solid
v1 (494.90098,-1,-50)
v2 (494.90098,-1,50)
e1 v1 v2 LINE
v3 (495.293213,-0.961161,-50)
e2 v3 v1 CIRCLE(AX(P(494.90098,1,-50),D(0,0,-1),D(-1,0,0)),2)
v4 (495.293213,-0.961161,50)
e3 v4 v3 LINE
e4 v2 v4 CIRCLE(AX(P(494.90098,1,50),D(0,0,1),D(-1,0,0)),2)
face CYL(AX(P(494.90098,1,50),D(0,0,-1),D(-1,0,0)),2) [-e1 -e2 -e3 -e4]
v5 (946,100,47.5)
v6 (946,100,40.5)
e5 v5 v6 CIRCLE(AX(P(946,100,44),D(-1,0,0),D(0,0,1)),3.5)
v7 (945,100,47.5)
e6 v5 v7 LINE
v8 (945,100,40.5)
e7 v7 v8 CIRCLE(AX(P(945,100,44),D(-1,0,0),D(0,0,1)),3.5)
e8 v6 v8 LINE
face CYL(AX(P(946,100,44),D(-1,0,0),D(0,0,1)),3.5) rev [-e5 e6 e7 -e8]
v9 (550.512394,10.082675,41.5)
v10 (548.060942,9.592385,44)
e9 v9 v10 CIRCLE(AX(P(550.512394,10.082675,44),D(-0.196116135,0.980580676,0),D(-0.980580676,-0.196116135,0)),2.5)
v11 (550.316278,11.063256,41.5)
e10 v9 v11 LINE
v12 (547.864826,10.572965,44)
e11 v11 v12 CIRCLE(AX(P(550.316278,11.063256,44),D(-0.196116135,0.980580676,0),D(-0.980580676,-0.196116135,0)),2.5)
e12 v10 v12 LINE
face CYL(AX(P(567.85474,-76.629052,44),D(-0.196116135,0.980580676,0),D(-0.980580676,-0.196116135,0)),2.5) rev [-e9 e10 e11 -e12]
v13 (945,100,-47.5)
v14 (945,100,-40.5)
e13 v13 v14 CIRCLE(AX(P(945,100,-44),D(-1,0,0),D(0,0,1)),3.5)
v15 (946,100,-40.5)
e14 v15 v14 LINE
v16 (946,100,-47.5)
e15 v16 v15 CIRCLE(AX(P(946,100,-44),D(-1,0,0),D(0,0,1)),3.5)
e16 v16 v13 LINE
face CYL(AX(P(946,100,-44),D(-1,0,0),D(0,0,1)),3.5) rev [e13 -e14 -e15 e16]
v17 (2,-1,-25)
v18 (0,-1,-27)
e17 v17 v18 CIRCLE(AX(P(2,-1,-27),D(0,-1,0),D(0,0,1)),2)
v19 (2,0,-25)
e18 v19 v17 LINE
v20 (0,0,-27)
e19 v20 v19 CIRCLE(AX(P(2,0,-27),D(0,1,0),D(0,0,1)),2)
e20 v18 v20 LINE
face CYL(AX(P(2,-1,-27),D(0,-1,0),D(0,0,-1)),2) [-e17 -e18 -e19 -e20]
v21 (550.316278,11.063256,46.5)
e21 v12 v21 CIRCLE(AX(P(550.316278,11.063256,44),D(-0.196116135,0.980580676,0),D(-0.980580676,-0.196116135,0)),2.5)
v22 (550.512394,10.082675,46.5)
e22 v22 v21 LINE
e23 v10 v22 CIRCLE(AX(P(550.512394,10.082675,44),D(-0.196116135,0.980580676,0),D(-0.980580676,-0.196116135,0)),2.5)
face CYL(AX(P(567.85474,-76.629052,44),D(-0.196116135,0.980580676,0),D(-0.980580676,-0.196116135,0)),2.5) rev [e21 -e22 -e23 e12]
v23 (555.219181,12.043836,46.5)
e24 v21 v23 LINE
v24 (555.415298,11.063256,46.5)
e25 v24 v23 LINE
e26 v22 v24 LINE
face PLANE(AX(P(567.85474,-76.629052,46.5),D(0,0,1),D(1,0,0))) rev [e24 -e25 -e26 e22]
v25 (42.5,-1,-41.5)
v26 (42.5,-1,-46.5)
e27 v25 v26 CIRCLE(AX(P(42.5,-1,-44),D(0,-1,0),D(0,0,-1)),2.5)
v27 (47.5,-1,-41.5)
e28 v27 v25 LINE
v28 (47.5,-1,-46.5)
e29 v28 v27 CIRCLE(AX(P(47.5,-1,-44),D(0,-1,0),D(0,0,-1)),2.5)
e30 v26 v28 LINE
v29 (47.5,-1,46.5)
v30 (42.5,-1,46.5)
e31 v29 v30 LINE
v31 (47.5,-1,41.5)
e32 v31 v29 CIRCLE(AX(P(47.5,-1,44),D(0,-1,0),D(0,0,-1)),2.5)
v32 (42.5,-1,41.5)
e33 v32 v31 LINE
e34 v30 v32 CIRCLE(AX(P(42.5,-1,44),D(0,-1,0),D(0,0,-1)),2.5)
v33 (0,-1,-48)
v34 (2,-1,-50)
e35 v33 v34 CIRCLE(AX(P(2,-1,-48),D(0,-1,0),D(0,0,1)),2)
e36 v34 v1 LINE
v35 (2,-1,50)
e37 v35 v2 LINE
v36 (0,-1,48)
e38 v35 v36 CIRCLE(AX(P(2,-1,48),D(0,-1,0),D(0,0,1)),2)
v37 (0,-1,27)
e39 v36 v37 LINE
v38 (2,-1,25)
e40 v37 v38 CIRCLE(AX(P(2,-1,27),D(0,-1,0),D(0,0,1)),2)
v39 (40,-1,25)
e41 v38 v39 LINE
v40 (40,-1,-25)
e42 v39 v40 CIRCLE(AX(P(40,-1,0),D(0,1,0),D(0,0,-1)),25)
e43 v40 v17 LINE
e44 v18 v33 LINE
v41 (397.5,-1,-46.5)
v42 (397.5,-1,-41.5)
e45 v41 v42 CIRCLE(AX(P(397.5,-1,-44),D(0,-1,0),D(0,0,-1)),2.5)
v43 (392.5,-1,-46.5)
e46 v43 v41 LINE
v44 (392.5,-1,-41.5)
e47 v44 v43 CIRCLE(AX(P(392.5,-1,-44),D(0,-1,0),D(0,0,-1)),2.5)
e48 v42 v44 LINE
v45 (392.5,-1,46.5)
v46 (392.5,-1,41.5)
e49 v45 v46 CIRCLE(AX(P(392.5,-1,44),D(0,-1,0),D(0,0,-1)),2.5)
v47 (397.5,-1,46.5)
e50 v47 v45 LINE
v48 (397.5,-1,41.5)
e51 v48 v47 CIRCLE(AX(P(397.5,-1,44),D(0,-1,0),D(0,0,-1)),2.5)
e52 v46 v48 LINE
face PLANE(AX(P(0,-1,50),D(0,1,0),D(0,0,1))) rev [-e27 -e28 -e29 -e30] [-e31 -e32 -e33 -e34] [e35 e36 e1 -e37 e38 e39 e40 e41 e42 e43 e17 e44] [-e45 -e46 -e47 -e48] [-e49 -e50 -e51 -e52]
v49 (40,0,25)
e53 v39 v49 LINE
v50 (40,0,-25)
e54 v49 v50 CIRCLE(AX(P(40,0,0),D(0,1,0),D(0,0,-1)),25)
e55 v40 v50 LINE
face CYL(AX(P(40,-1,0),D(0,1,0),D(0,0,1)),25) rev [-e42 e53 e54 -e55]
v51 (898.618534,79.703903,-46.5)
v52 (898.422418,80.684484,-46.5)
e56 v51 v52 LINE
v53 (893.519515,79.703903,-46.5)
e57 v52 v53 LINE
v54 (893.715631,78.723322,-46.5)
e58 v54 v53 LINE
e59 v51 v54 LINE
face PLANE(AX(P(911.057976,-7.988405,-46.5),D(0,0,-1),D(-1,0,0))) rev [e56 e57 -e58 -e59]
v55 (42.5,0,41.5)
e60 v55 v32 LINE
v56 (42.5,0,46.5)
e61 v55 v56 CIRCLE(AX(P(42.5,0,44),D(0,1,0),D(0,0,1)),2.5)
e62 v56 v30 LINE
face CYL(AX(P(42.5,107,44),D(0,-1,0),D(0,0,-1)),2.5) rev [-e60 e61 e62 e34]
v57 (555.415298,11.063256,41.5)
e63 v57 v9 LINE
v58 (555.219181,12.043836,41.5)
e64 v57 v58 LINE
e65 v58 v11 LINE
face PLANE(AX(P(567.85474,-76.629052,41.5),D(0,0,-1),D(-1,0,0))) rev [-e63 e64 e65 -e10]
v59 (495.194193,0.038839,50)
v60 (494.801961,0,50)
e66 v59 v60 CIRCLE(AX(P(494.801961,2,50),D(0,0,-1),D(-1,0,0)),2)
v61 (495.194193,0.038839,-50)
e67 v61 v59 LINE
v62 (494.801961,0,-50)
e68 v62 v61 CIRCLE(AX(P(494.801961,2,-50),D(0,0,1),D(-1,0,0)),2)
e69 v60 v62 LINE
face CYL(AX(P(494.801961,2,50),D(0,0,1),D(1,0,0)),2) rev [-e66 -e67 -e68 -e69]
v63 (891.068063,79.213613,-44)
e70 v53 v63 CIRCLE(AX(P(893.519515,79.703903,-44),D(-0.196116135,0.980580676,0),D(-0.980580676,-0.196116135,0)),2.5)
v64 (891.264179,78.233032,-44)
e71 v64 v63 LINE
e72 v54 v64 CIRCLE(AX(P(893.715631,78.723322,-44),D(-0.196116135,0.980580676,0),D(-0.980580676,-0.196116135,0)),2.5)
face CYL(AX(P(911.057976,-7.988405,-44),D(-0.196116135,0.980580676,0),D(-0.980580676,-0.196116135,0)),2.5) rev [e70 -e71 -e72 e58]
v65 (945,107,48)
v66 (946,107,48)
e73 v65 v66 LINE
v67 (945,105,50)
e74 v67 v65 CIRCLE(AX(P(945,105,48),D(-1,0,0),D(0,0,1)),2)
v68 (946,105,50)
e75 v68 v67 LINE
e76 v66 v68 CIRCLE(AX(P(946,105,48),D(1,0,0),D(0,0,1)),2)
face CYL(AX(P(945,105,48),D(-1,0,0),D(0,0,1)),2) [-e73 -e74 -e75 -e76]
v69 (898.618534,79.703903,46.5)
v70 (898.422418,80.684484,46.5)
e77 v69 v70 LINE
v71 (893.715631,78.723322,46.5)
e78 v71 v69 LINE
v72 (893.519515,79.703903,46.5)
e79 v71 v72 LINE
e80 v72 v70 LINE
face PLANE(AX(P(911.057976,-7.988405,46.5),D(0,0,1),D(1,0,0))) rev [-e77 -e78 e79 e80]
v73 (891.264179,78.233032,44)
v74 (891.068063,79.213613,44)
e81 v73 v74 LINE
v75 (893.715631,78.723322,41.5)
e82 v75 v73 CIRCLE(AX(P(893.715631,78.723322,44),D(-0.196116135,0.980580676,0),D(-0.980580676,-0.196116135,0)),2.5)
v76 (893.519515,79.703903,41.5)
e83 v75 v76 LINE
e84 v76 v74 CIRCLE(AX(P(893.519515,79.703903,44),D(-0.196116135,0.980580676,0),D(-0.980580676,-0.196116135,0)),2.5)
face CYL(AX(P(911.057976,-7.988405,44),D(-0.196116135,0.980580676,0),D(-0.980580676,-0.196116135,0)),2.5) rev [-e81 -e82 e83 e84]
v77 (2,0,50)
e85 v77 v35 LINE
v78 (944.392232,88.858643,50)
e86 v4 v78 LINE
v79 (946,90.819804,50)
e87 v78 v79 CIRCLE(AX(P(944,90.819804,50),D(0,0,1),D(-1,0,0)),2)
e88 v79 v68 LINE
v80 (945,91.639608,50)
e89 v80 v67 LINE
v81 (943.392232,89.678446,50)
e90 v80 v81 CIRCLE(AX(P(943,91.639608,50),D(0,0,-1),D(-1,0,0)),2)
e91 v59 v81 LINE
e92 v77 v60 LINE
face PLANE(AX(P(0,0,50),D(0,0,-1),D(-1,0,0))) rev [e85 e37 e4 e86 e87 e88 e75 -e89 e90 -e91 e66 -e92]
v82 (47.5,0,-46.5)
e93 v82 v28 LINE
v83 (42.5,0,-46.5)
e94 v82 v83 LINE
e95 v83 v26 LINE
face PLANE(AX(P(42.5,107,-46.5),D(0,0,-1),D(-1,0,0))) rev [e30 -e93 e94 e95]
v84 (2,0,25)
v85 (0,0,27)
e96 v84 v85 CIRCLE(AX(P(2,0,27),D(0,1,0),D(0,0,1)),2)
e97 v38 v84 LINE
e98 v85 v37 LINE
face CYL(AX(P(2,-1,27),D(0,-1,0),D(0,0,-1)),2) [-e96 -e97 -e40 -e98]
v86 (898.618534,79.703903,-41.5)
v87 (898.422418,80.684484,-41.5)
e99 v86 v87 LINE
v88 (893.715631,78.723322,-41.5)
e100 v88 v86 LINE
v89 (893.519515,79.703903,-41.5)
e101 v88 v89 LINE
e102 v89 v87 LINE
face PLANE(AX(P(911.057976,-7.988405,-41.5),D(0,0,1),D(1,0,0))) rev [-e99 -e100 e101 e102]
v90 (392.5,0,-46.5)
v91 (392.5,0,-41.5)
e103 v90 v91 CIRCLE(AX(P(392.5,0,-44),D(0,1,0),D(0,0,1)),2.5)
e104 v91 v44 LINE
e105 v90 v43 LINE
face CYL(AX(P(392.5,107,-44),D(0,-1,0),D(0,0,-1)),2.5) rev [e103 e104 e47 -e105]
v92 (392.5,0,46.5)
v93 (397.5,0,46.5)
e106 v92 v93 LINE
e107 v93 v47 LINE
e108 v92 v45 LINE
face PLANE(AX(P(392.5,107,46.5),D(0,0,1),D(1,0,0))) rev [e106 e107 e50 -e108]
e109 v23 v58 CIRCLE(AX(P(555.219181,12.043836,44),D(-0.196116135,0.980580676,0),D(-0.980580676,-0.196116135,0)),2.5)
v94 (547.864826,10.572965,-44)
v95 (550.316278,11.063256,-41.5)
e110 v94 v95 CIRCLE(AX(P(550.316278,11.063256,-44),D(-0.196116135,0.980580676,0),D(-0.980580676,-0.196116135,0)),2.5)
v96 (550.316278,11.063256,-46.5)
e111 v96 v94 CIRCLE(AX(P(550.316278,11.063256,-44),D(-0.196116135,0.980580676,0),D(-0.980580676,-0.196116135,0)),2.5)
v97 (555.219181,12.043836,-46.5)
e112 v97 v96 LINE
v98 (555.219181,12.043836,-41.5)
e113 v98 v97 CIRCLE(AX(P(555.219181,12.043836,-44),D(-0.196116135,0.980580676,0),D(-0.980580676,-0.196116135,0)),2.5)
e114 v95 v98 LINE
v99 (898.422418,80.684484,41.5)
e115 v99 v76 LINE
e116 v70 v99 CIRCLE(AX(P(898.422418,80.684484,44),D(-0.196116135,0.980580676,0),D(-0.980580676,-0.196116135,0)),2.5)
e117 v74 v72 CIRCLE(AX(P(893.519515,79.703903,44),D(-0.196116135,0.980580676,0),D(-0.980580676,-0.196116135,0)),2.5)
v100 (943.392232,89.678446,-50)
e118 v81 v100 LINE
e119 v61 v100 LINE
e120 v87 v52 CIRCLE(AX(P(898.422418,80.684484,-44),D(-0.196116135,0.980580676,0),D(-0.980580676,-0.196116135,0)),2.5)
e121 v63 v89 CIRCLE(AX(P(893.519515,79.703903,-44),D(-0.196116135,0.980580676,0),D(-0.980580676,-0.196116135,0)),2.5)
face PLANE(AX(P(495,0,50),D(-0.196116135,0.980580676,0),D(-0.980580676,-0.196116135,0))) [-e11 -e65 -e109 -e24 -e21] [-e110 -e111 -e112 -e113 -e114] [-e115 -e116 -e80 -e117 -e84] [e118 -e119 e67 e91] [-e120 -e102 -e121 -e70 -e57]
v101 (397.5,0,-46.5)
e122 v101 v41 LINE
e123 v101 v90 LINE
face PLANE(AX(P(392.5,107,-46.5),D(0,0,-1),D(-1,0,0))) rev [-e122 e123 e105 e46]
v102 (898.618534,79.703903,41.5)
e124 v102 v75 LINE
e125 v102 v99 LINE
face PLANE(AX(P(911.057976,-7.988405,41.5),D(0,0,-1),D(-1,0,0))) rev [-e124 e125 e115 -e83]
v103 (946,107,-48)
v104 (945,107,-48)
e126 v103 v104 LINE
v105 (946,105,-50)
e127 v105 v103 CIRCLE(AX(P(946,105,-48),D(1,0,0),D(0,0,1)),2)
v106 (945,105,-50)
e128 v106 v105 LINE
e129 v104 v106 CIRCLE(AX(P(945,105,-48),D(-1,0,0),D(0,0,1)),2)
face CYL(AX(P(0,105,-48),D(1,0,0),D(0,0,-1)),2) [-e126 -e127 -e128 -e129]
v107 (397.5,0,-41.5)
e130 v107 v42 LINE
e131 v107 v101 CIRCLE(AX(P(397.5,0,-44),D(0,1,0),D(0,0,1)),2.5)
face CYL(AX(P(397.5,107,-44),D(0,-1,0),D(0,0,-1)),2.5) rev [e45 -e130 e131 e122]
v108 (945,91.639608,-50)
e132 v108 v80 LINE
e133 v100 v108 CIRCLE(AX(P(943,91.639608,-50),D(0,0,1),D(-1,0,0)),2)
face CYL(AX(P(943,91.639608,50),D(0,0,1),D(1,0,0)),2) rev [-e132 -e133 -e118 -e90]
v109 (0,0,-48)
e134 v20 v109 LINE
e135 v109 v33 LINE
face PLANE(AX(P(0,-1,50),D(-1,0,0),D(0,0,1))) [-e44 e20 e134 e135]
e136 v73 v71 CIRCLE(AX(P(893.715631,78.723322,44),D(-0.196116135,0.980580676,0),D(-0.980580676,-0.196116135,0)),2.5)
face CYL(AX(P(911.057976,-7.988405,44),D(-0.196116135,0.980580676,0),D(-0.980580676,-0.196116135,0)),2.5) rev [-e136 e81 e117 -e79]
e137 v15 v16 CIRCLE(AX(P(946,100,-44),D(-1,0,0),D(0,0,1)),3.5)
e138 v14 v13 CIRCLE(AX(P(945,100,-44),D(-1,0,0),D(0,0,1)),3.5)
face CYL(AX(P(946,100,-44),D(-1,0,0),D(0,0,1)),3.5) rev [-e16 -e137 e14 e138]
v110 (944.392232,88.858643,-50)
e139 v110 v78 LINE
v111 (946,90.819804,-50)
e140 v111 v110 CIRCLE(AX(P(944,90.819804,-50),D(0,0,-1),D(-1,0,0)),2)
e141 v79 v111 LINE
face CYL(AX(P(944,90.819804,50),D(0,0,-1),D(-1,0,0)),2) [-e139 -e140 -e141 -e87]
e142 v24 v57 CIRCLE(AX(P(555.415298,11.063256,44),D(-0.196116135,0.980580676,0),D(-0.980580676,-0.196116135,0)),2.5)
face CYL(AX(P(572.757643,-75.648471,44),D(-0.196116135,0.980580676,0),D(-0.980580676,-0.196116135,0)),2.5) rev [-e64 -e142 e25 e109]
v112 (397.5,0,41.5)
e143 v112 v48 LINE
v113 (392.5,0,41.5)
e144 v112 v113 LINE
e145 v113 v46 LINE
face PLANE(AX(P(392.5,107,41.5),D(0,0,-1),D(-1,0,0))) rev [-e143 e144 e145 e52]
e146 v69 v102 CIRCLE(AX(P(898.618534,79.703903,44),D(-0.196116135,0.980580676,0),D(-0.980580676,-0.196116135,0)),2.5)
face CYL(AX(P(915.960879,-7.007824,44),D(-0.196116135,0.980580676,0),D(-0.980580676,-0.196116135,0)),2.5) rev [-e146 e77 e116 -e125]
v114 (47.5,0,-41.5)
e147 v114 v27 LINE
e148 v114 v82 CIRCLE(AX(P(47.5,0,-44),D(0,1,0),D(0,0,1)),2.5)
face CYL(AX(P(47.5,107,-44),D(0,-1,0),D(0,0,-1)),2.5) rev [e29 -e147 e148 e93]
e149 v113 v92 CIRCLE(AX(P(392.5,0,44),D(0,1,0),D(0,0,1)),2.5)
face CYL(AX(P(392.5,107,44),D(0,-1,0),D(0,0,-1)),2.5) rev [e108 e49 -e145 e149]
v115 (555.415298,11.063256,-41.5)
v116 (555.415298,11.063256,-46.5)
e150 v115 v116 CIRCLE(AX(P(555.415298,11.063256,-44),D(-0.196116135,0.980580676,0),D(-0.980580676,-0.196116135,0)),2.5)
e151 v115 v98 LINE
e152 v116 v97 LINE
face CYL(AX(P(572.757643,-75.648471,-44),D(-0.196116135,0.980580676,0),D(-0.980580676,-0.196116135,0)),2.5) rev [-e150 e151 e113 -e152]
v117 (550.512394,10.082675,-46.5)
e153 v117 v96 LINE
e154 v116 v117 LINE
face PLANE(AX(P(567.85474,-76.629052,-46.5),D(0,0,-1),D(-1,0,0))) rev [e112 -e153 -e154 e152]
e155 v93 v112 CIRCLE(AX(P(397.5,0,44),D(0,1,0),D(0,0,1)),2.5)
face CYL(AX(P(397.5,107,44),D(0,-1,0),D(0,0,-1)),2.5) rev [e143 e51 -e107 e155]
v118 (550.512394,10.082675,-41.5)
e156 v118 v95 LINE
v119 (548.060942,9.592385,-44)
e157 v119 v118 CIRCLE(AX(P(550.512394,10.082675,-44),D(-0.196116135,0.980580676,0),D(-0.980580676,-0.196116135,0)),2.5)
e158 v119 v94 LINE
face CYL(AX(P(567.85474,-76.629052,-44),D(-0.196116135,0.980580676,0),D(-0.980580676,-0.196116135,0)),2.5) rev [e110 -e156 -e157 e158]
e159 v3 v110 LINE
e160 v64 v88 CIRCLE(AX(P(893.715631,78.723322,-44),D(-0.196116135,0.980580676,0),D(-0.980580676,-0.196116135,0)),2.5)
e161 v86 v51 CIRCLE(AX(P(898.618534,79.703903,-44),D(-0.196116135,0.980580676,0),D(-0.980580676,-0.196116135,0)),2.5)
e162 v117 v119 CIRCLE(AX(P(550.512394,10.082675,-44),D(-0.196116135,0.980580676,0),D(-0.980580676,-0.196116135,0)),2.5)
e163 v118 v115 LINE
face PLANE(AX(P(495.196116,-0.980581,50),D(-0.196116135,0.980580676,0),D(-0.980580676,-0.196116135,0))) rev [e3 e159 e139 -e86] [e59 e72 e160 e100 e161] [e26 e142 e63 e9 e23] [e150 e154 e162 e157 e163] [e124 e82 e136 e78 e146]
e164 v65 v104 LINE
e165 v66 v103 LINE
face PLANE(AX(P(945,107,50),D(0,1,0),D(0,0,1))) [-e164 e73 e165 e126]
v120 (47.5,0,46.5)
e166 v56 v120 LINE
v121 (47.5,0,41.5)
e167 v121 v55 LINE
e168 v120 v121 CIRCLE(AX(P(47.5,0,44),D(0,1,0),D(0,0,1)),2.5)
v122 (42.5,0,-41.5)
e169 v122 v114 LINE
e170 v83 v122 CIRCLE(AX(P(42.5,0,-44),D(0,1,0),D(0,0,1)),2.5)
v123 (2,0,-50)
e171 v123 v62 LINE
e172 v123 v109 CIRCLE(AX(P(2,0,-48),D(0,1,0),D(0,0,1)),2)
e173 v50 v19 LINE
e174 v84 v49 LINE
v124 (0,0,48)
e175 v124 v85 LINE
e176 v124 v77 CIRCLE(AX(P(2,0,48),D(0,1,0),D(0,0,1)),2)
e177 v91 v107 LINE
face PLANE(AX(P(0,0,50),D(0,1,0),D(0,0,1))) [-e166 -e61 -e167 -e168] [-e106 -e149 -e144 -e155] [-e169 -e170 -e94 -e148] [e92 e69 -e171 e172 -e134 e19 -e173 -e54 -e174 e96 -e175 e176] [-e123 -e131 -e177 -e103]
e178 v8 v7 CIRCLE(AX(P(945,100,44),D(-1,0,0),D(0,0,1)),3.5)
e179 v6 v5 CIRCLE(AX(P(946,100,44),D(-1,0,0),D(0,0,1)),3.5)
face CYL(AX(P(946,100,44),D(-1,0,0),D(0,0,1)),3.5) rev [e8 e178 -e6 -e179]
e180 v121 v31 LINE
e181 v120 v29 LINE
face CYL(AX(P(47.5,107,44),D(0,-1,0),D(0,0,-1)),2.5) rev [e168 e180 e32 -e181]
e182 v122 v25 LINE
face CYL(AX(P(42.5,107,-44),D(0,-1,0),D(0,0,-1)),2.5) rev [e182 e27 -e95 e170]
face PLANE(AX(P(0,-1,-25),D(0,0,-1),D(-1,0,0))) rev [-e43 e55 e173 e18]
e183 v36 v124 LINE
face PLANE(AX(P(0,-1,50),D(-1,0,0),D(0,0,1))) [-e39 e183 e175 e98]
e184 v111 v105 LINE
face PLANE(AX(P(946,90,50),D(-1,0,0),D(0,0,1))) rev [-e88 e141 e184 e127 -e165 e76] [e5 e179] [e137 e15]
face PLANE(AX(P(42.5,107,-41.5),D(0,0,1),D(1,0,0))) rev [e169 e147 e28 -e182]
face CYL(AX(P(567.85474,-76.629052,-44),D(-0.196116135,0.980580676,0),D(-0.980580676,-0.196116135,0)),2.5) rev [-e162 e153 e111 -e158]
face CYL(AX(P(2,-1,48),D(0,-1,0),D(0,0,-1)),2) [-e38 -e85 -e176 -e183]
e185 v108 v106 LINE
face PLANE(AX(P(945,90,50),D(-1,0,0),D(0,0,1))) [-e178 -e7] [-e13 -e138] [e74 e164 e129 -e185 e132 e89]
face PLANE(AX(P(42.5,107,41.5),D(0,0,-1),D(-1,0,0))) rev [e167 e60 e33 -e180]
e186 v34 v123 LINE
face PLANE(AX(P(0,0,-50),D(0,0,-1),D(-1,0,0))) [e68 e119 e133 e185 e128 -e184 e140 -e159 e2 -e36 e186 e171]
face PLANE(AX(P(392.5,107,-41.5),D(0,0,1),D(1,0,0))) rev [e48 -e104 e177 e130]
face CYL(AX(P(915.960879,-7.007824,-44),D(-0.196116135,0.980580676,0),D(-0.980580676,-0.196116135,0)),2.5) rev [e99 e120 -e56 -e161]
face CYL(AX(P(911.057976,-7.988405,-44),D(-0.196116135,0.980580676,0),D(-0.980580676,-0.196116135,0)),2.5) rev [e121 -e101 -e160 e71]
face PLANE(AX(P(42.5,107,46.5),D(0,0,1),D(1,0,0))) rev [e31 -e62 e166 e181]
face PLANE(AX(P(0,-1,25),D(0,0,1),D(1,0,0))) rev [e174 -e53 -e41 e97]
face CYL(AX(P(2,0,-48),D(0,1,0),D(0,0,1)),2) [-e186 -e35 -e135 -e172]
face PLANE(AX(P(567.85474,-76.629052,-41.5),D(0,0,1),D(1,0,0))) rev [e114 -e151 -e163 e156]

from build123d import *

# Parameters (mm, degrees)
EXTRUDE_THIN1_DEPTH = 50
SKETCH2_R           = 3.5
CUT_EXTRUDE1_DEPTH  = 953.351825745
CUT_EXTRUDE2_DEPTH  = 954.456868453
CUT_EXTRUDE3_DEPTH  = 951.073377733
CUT_EXTRUDE4_DEPTH  = 954.344114158
FILLET1_R           = 2


with BuildPart() as part:
    # Sketch1 → Extrude-Thin1 (new, symmetric)
    with BuildSketch(Plane.XY):
        Polygon((0, 0), (495, 0), (945, 90), (945, 107), (946, 107), (946, 89.180196097), (495.099019514, -1), (0, -1), align=None)
    extrude(amount=EXTRUDE_THIN1_DEPTH, both=True)

    # Sketch2 → Cut-Extrude1 (cut, through all)
    with BuildSketch(Plane.ZY.offset(-945)):
        with Locations((-44, 100)):
            Circle(SKETCH2_R)
        with Locations((44, 100)):
            Circle(SKETCH2_R)
    extrude(amount=-CUT_EXTRUDE1_DEPTH, mode=Mode.SUBTRACT)

    # Sketch3 → Cut-Extrude2 (cut, through all)
    with BuildSketch(Plane.XZ.offset(1)):
        with BuildLine():
            Line((42.5, 46.5), (47.5, 46.5))
            ThreePointArc((47.5, 46.5), (50, 44), (47.5, 41.5))
            Line((47.5, 41.5), (42.5, 41.5))
            ThreePointArc((42.5, 41.5), (40, 44), (42.5, 46.5))
        make_face()
        with BuildLine():
            Line((42.5, -41.5), (47.5, -41.5))
            ThreePointArc((47.5, -41.5), (50, -44), (47.5, -46.5))
            Line((47.5, -46.5), (42.5, -46.5))
            ThreePointArc((42.5, -46.5), (40, -44), (42.5, -41.5))
        make_face()
        with BuildLine():
            Line((392.5, -41.5), (397.5, -41.5))
            ThreePointArc((397.5, -41.5), (400, -44), (397.5, -46.5))
            Line((397.5, -46.5), (392.5, -46.5))
            ThreePointArc((392.5, -46.5), (390, -44), (392.5, -41.5))
        make_face()
        with BuildLine():
            Line((392.5, 46.5), (397.5, 46.5))
            ThreePointArc((397.5, 46.5), (400, 44), (397.5, 41.5))
            Line((397.5, 41.5), (392.5, 41.5))
            ThreePointArc((392.5, 41.5), (390, 44), (392.5, 46.5))
        make_face()
    extrude(amount=-CUT_EXTRUDE2_DEPTH, mode=Mode.SUBTRACT)

    # Sketch4 → Cut-Extrude3 (cut, through all)
    with BuildSketch(Plane(origin=(19.038461538, -95.192307692, 0), x_dir=(0.9805806756909202, 0.1961161351381841, 0), z_dir=(-0.1961161351381841, 0.9805806756909202, 0))):
        with BuildLine():
            Line((541.79919069, 46.5), (546.79919069, 46.5))
            ThreePointArc((546.79919069, 46.5), (549.29919069, 44), (546.79919069, 41.5))
            Line((546.79919069, 41.5), (541.79919069, 41.5))
            ThreePointArc((541.79919069, 41.5), (539.29919069, 44), (541.79919069, 46.5))
        make_face()
        with BuildLine():
            Line((541.79919069, -41.5), (546.79919069, -41.5))
            ThreePointArc((546.79919069, -41.5), (549.29919069, -44), (546.79919069, -46.5))
            Line((546.79919069, -46.5), (541.79919069, -46.5))
            ThreePointArc((541.79919069, -46.5), (539.29919069, -44), (541.79919069, -41.5))
        make_face()
        with BuildLine():
            Line((891.79919069, -41.5), (896.79919069, -41.5))
            ThreePointArc((896.79919069, -41.5), (899.29919069, -44), (896.79919069, -46.5))
            Line((896.79919069, -46.5), (891.79919069, -46.5))
            ThreePointArc((891.79919069, -46.5), (889.29919069, -44), (891.79919069, -41.5))
        make_face()
        with BuildLine():
            Line((891.79919069, 46.5), (896.79919069, 46.5))
            ThreePointArc((896.79919069, 46.5), (899.29919069, 44), (896.79919069, 41.5))
            Line((896.79919069, 41.5), (891.79919069, 41.5))
            ThreePointArc((891.79919069, 41.5), (889.29919069, 44), (891.79919069, 46.5))
        make_face()
    extrude(amount=-CUT_EXTRUDE3_DEPTH, mode=Mode.SUBTRACT)

    # Sketch5 → Cut-Extrude4 (cut, through all)
    with BuildSketch(Plane(origin=(0, 0, 0), x_dir=(1, 0, 0), z_dir=(0, 1, 0))):
        with BuildLine():
            Line((0, -25), (40, -25))
            ThreePointArc((40, -25), (65, 0), (40, 25))
            Line((40, 25), (0, 25))
            Line((0, 25), (0, -25))
        make_face()
    extrude(amount=-CUT_EXTRUDE4_DEPTH, mode=Mode.SUBTRACT)

    # Fillet1
    fillet1_edges = [part.edges().sort_by_distance(p)[0] for p in [
        (946, 89.180196097, 0),
        (495.099019514, -1, 0),
        (495, 0, 0),
        (945, 90, 0),
        (0, -0.5, 25),
        (0, -0.5, -25),
        (0, -0.5, 50),
        (945.5, 107, 50),
        (0, -0.5, -50),
        (945.5, 107, -50),
    ]]
    fillet(fillet1_edges, radius=FILLET1_R)


solid = part.part
